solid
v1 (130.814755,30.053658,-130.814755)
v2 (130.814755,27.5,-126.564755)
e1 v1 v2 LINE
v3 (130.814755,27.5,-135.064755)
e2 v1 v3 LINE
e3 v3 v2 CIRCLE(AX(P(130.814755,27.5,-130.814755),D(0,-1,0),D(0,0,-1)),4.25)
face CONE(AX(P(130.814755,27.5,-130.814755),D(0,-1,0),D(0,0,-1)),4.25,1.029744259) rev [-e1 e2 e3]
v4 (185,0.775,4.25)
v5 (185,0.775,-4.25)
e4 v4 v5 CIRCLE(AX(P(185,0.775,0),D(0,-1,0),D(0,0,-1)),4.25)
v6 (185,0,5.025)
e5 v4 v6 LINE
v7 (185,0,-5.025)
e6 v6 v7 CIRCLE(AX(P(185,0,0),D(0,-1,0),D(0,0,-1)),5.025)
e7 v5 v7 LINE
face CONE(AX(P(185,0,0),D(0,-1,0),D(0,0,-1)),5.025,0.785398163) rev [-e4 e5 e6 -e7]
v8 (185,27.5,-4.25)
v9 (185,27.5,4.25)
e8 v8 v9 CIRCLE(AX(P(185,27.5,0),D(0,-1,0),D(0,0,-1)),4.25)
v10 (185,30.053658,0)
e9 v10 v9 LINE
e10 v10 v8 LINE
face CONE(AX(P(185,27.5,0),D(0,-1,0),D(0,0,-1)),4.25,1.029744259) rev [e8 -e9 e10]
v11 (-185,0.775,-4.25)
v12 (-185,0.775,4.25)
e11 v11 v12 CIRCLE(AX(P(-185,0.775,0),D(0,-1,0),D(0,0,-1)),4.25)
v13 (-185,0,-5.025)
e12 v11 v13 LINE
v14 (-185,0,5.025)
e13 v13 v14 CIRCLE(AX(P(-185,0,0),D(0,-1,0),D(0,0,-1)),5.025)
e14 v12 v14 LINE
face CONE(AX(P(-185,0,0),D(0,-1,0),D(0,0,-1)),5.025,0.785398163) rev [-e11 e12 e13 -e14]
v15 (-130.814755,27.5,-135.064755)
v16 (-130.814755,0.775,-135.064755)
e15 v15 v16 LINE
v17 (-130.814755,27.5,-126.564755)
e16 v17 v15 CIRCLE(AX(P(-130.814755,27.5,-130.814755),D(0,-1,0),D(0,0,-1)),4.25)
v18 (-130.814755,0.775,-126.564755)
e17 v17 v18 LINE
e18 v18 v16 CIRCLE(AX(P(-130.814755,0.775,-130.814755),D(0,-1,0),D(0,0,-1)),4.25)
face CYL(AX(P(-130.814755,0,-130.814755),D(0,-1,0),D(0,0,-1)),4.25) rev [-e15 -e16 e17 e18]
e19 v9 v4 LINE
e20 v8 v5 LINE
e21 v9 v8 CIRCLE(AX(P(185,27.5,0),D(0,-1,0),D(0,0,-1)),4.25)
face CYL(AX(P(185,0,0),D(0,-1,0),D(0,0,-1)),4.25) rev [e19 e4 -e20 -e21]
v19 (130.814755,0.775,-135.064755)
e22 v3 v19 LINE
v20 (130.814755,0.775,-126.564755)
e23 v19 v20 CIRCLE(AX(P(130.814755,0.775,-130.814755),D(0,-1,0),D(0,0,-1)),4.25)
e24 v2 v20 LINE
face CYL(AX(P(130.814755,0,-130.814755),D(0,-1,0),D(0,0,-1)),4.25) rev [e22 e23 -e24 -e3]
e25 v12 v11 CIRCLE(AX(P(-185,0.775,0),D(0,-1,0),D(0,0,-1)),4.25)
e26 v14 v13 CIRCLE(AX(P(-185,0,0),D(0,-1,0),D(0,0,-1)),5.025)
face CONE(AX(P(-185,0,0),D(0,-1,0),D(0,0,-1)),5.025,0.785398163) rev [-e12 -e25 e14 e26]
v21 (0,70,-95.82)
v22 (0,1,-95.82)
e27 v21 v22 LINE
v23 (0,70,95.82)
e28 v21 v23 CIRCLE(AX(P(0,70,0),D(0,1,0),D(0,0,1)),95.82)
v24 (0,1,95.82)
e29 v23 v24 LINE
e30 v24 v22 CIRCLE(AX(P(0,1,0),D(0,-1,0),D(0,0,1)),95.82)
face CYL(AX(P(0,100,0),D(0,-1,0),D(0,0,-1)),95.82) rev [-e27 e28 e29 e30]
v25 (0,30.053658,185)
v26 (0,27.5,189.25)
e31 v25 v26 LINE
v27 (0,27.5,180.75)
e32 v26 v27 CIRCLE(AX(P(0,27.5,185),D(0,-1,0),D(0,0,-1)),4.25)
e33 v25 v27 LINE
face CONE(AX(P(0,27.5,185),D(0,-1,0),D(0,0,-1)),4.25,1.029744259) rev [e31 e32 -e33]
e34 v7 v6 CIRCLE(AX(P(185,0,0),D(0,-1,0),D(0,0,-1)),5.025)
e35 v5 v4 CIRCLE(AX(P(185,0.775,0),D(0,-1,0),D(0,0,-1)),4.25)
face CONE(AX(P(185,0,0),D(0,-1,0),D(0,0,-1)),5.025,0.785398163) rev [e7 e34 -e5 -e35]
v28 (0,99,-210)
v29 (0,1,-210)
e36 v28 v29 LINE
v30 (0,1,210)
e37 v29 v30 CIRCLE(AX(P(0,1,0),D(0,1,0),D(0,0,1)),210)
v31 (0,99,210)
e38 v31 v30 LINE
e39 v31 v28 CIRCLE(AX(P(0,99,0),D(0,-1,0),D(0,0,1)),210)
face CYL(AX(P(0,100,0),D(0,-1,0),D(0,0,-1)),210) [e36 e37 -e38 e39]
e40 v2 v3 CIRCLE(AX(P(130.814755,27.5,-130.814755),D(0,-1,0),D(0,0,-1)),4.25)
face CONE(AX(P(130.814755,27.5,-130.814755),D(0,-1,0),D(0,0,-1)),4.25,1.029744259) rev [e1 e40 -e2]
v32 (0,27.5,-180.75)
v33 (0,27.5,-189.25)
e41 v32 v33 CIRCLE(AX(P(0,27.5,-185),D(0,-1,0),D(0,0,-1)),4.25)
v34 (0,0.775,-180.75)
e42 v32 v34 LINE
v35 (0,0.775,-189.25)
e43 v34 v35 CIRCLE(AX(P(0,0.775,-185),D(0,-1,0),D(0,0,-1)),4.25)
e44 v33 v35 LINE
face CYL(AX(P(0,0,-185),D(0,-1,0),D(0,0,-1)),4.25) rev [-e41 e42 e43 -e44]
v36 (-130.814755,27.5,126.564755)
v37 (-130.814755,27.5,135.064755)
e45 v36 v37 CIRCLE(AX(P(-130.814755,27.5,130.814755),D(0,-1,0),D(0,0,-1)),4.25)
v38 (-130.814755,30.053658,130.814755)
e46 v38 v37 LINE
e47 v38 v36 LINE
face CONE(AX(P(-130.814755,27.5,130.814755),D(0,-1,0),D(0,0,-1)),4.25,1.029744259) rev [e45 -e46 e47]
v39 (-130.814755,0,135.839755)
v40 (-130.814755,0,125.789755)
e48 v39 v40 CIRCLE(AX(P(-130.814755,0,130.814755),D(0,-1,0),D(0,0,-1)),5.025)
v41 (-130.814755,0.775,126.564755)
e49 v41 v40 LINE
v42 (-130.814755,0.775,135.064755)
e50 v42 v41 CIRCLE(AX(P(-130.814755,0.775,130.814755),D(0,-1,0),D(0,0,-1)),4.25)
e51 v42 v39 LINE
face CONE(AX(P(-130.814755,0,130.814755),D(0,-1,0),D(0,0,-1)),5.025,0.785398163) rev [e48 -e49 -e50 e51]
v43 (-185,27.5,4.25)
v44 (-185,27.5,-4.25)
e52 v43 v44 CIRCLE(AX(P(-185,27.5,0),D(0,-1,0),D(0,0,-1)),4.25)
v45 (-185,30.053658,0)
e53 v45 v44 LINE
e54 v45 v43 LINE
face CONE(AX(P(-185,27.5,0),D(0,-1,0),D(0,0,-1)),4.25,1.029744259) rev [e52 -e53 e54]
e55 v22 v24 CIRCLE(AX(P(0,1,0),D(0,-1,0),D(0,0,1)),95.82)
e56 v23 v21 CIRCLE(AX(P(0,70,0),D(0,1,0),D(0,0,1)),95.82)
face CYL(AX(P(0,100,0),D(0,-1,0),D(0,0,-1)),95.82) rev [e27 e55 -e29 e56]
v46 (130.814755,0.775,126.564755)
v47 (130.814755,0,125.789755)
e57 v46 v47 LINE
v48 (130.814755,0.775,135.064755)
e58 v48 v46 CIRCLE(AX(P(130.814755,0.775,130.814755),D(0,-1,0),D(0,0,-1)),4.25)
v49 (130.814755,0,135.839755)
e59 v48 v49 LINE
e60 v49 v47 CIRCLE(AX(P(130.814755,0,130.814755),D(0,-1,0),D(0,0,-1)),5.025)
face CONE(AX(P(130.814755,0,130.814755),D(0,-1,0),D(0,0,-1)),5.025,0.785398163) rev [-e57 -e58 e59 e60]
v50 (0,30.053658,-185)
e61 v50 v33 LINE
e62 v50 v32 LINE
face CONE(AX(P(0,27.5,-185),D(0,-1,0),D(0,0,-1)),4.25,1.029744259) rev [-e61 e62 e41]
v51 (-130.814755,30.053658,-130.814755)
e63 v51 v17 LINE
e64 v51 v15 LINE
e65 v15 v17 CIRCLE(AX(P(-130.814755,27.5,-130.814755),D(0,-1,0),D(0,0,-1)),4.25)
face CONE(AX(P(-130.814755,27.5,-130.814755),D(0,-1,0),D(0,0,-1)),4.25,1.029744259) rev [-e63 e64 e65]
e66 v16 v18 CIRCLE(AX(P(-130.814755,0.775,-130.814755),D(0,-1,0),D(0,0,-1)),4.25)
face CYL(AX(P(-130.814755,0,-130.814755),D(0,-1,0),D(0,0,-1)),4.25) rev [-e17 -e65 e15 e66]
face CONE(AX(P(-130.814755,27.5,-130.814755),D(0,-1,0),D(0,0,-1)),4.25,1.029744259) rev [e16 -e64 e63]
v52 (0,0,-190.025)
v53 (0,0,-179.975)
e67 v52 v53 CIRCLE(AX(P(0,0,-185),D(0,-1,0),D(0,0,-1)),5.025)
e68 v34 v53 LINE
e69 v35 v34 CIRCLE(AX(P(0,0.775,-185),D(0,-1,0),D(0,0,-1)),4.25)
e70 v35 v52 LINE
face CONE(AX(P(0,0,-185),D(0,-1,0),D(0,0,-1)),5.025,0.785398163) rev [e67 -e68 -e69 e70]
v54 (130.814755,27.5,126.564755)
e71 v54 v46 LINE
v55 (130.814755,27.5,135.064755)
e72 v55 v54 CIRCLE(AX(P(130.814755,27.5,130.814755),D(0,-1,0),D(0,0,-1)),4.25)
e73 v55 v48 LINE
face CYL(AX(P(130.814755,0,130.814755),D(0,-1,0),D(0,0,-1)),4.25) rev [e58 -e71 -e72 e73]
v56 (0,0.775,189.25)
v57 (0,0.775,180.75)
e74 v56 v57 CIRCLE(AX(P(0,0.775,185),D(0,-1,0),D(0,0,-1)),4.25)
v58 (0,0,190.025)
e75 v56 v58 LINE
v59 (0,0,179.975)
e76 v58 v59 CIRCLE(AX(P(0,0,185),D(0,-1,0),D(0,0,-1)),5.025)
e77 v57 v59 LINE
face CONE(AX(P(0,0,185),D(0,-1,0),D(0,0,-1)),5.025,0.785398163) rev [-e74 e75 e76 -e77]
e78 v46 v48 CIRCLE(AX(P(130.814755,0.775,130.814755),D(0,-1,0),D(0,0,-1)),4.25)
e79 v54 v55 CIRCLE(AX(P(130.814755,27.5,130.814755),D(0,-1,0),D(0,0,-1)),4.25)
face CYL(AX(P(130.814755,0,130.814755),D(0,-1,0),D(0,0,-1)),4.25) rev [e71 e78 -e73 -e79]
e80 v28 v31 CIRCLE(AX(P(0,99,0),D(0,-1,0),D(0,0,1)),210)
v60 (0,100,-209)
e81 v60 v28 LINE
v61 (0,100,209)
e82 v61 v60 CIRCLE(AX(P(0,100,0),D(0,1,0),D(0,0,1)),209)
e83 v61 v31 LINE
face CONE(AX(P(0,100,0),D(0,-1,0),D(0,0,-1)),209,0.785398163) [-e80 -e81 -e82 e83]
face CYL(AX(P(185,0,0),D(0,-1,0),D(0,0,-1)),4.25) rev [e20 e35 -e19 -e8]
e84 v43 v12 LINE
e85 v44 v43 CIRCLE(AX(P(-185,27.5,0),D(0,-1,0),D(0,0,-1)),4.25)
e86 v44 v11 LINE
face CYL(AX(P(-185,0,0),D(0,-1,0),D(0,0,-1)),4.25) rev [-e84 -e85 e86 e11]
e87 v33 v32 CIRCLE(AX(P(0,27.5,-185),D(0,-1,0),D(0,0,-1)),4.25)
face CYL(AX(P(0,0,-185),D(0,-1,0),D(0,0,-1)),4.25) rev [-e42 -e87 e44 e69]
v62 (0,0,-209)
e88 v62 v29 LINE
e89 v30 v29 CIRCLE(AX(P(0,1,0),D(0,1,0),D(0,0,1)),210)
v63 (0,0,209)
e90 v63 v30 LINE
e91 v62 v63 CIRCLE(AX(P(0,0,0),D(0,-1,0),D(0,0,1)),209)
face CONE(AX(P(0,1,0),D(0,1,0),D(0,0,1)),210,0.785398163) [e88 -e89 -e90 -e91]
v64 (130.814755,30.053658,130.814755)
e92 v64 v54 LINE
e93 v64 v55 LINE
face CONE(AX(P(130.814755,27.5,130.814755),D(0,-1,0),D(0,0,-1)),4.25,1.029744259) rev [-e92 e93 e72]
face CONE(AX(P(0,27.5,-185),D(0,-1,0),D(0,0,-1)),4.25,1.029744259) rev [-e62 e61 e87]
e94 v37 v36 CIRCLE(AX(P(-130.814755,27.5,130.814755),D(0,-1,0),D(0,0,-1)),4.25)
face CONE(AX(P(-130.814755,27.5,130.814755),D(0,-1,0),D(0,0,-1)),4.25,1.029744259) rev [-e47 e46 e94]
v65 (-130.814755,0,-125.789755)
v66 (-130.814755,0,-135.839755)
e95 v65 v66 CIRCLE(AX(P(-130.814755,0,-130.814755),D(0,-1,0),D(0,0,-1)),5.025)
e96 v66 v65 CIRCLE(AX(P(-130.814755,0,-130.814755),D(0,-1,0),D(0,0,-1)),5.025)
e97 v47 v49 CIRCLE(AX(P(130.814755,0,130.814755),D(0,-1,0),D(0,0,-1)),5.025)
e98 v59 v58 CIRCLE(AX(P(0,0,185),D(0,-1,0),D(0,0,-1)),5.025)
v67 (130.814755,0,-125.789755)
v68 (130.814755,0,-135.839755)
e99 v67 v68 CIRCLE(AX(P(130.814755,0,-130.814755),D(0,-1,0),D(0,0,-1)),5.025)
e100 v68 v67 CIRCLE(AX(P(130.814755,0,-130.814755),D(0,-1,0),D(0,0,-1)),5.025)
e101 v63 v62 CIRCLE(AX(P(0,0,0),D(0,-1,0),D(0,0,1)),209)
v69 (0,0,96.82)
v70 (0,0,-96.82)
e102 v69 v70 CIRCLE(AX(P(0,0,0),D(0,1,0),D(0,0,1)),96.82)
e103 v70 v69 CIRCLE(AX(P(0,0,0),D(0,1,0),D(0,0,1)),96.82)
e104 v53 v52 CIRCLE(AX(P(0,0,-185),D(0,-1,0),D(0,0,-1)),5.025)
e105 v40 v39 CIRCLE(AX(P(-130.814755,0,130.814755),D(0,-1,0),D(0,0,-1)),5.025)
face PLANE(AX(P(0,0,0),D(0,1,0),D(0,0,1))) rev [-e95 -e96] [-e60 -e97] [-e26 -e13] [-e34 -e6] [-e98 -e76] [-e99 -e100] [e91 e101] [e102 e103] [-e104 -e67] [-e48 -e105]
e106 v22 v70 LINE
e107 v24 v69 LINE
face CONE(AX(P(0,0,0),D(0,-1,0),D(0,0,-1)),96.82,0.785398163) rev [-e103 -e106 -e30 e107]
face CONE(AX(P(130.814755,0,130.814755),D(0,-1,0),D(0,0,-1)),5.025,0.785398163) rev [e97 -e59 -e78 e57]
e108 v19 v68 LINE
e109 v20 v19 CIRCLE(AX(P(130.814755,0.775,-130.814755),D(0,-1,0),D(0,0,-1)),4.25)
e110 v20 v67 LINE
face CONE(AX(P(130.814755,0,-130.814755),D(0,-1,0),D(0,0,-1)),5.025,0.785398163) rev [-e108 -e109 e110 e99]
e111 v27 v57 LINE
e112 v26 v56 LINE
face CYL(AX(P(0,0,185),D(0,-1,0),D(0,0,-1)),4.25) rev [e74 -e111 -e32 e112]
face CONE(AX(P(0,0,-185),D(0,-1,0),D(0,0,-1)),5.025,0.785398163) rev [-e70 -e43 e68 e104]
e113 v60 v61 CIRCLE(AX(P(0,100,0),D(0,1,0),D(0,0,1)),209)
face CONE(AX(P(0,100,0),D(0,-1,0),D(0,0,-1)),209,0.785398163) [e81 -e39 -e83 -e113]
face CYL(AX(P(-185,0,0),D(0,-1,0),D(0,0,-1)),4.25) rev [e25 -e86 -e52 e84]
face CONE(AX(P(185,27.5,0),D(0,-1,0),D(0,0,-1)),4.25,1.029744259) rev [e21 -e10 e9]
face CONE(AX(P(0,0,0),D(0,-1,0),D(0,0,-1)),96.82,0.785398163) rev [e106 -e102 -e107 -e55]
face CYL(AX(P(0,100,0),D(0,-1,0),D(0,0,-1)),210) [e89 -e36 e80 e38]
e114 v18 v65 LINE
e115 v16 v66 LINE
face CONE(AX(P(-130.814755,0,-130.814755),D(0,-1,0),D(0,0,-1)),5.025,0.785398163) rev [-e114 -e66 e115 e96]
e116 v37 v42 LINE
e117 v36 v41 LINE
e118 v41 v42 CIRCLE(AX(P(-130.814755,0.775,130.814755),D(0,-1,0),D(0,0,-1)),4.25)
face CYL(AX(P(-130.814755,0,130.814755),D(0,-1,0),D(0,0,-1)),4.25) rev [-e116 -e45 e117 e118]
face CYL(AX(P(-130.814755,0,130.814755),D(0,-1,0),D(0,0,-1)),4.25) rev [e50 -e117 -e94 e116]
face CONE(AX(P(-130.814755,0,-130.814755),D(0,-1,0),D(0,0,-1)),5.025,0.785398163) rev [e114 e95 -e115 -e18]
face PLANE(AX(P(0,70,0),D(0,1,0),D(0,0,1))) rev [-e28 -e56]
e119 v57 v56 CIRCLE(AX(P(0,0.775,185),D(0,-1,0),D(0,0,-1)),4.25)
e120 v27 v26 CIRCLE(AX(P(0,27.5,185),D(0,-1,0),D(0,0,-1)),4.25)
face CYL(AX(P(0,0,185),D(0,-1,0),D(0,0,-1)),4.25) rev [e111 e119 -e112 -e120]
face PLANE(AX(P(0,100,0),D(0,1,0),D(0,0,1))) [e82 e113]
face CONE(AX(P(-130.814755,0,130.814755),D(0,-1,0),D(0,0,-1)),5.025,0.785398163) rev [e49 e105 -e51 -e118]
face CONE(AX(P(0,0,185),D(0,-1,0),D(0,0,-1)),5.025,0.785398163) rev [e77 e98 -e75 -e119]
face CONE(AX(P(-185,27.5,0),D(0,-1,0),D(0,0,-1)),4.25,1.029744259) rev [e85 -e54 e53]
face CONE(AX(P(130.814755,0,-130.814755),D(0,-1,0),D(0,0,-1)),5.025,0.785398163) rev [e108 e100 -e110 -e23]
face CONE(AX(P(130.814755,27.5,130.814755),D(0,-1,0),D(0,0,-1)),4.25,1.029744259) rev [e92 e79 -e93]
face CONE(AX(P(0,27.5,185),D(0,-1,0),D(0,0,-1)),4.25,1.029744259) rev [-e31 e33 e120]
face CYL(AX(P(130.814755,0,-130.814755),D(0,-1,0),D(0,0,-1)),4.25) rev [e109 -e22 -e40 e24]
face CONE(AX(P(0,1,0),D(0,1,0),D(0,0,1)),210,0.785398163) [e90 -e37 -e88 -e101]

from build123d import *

# Parameters (mm, degrees)
SKETCH_1_R               = 210
SKETCH_1_R_2             = 95.82
EXTRUDE_1_DEPTH          = 100
SKETCH_5_R               = 150
EXTRUDE_4_DEPTH          = 30
PATTERN_CIRCULAR_1_COUNT = 8
CHAMFER_1_SIZE           = 1


with BuildPart() as part:
    # 草图1 → 凸台-拉伸1 (new body)
    with BuildSketch(Plane(origin=(0, 0, 0), x_dir=(1, 0, 0), z_dir=(0, 1, 0))):
        with Locations(Location((0, 0, 0), (0, 0, 270))):
            Circle(SKETCH_1_R)
        with Locations(Location((0, 0, 0), (0, 0, 270))):
            Circle(SKETCH_1_R_2, mode=Mode.SUBTRACT)
    extrude(amount=EXTRUDE_1_DEPTH)

    # 草图5 → 凸台-拉伸4 (add)
    with BuildSketch(Plane(origin=(0, 100, 0), x_dir=(1, 0, 0), z_dir=(0, 1, 0))):
        Circle(SKETCH_5_R)
    extrude(amount=-EXTRUDE_4_DEPTH)

    # 草图8 → M10 螺纹孔1 (revolve, cut)
    with BuildSketch(Plane(origin=(185, 0, 0), x_dir=(0, 0, -1), z_dir=(1, 0, 0))):
        Polygon((0, 0), (0, 30.053657631), (4.25, 27.5), (4.25, 0.775), (5.025, 0), align=None)
    hole_wizard_m10_1 = revolve(axis=Axis((185, -6.35, 0), (0, 1, 0)), mode=Mode.SUBTRACT)

    # 阵列(圆周)1: M10 螺纹孔1 ×8 about axis
    pattern_circular_1_axis = Axis((0, 0, 0), (0, 1, 0))
    for i in range(1, PATTERN_CIRCULAR_1_COUNT):
        add(hole_wizard_m10_1.rotate(pattern_circular_1_axis, i * 360 / PATTERN_CIRCULAR_1_COUNT), mode=Mode.SUBTRACT)

    # 倒角1
    chamfer_1_edges = [part.edges().sort_by_distance(p)[0] for p in [
        (0, 0, -210),
        (0, 100, -210),
        (0, 0, -95.82),
    ]]
    chamfer(chamfer_1_edges, length=CHAMFER_1_SIZE)


solid = part.part
